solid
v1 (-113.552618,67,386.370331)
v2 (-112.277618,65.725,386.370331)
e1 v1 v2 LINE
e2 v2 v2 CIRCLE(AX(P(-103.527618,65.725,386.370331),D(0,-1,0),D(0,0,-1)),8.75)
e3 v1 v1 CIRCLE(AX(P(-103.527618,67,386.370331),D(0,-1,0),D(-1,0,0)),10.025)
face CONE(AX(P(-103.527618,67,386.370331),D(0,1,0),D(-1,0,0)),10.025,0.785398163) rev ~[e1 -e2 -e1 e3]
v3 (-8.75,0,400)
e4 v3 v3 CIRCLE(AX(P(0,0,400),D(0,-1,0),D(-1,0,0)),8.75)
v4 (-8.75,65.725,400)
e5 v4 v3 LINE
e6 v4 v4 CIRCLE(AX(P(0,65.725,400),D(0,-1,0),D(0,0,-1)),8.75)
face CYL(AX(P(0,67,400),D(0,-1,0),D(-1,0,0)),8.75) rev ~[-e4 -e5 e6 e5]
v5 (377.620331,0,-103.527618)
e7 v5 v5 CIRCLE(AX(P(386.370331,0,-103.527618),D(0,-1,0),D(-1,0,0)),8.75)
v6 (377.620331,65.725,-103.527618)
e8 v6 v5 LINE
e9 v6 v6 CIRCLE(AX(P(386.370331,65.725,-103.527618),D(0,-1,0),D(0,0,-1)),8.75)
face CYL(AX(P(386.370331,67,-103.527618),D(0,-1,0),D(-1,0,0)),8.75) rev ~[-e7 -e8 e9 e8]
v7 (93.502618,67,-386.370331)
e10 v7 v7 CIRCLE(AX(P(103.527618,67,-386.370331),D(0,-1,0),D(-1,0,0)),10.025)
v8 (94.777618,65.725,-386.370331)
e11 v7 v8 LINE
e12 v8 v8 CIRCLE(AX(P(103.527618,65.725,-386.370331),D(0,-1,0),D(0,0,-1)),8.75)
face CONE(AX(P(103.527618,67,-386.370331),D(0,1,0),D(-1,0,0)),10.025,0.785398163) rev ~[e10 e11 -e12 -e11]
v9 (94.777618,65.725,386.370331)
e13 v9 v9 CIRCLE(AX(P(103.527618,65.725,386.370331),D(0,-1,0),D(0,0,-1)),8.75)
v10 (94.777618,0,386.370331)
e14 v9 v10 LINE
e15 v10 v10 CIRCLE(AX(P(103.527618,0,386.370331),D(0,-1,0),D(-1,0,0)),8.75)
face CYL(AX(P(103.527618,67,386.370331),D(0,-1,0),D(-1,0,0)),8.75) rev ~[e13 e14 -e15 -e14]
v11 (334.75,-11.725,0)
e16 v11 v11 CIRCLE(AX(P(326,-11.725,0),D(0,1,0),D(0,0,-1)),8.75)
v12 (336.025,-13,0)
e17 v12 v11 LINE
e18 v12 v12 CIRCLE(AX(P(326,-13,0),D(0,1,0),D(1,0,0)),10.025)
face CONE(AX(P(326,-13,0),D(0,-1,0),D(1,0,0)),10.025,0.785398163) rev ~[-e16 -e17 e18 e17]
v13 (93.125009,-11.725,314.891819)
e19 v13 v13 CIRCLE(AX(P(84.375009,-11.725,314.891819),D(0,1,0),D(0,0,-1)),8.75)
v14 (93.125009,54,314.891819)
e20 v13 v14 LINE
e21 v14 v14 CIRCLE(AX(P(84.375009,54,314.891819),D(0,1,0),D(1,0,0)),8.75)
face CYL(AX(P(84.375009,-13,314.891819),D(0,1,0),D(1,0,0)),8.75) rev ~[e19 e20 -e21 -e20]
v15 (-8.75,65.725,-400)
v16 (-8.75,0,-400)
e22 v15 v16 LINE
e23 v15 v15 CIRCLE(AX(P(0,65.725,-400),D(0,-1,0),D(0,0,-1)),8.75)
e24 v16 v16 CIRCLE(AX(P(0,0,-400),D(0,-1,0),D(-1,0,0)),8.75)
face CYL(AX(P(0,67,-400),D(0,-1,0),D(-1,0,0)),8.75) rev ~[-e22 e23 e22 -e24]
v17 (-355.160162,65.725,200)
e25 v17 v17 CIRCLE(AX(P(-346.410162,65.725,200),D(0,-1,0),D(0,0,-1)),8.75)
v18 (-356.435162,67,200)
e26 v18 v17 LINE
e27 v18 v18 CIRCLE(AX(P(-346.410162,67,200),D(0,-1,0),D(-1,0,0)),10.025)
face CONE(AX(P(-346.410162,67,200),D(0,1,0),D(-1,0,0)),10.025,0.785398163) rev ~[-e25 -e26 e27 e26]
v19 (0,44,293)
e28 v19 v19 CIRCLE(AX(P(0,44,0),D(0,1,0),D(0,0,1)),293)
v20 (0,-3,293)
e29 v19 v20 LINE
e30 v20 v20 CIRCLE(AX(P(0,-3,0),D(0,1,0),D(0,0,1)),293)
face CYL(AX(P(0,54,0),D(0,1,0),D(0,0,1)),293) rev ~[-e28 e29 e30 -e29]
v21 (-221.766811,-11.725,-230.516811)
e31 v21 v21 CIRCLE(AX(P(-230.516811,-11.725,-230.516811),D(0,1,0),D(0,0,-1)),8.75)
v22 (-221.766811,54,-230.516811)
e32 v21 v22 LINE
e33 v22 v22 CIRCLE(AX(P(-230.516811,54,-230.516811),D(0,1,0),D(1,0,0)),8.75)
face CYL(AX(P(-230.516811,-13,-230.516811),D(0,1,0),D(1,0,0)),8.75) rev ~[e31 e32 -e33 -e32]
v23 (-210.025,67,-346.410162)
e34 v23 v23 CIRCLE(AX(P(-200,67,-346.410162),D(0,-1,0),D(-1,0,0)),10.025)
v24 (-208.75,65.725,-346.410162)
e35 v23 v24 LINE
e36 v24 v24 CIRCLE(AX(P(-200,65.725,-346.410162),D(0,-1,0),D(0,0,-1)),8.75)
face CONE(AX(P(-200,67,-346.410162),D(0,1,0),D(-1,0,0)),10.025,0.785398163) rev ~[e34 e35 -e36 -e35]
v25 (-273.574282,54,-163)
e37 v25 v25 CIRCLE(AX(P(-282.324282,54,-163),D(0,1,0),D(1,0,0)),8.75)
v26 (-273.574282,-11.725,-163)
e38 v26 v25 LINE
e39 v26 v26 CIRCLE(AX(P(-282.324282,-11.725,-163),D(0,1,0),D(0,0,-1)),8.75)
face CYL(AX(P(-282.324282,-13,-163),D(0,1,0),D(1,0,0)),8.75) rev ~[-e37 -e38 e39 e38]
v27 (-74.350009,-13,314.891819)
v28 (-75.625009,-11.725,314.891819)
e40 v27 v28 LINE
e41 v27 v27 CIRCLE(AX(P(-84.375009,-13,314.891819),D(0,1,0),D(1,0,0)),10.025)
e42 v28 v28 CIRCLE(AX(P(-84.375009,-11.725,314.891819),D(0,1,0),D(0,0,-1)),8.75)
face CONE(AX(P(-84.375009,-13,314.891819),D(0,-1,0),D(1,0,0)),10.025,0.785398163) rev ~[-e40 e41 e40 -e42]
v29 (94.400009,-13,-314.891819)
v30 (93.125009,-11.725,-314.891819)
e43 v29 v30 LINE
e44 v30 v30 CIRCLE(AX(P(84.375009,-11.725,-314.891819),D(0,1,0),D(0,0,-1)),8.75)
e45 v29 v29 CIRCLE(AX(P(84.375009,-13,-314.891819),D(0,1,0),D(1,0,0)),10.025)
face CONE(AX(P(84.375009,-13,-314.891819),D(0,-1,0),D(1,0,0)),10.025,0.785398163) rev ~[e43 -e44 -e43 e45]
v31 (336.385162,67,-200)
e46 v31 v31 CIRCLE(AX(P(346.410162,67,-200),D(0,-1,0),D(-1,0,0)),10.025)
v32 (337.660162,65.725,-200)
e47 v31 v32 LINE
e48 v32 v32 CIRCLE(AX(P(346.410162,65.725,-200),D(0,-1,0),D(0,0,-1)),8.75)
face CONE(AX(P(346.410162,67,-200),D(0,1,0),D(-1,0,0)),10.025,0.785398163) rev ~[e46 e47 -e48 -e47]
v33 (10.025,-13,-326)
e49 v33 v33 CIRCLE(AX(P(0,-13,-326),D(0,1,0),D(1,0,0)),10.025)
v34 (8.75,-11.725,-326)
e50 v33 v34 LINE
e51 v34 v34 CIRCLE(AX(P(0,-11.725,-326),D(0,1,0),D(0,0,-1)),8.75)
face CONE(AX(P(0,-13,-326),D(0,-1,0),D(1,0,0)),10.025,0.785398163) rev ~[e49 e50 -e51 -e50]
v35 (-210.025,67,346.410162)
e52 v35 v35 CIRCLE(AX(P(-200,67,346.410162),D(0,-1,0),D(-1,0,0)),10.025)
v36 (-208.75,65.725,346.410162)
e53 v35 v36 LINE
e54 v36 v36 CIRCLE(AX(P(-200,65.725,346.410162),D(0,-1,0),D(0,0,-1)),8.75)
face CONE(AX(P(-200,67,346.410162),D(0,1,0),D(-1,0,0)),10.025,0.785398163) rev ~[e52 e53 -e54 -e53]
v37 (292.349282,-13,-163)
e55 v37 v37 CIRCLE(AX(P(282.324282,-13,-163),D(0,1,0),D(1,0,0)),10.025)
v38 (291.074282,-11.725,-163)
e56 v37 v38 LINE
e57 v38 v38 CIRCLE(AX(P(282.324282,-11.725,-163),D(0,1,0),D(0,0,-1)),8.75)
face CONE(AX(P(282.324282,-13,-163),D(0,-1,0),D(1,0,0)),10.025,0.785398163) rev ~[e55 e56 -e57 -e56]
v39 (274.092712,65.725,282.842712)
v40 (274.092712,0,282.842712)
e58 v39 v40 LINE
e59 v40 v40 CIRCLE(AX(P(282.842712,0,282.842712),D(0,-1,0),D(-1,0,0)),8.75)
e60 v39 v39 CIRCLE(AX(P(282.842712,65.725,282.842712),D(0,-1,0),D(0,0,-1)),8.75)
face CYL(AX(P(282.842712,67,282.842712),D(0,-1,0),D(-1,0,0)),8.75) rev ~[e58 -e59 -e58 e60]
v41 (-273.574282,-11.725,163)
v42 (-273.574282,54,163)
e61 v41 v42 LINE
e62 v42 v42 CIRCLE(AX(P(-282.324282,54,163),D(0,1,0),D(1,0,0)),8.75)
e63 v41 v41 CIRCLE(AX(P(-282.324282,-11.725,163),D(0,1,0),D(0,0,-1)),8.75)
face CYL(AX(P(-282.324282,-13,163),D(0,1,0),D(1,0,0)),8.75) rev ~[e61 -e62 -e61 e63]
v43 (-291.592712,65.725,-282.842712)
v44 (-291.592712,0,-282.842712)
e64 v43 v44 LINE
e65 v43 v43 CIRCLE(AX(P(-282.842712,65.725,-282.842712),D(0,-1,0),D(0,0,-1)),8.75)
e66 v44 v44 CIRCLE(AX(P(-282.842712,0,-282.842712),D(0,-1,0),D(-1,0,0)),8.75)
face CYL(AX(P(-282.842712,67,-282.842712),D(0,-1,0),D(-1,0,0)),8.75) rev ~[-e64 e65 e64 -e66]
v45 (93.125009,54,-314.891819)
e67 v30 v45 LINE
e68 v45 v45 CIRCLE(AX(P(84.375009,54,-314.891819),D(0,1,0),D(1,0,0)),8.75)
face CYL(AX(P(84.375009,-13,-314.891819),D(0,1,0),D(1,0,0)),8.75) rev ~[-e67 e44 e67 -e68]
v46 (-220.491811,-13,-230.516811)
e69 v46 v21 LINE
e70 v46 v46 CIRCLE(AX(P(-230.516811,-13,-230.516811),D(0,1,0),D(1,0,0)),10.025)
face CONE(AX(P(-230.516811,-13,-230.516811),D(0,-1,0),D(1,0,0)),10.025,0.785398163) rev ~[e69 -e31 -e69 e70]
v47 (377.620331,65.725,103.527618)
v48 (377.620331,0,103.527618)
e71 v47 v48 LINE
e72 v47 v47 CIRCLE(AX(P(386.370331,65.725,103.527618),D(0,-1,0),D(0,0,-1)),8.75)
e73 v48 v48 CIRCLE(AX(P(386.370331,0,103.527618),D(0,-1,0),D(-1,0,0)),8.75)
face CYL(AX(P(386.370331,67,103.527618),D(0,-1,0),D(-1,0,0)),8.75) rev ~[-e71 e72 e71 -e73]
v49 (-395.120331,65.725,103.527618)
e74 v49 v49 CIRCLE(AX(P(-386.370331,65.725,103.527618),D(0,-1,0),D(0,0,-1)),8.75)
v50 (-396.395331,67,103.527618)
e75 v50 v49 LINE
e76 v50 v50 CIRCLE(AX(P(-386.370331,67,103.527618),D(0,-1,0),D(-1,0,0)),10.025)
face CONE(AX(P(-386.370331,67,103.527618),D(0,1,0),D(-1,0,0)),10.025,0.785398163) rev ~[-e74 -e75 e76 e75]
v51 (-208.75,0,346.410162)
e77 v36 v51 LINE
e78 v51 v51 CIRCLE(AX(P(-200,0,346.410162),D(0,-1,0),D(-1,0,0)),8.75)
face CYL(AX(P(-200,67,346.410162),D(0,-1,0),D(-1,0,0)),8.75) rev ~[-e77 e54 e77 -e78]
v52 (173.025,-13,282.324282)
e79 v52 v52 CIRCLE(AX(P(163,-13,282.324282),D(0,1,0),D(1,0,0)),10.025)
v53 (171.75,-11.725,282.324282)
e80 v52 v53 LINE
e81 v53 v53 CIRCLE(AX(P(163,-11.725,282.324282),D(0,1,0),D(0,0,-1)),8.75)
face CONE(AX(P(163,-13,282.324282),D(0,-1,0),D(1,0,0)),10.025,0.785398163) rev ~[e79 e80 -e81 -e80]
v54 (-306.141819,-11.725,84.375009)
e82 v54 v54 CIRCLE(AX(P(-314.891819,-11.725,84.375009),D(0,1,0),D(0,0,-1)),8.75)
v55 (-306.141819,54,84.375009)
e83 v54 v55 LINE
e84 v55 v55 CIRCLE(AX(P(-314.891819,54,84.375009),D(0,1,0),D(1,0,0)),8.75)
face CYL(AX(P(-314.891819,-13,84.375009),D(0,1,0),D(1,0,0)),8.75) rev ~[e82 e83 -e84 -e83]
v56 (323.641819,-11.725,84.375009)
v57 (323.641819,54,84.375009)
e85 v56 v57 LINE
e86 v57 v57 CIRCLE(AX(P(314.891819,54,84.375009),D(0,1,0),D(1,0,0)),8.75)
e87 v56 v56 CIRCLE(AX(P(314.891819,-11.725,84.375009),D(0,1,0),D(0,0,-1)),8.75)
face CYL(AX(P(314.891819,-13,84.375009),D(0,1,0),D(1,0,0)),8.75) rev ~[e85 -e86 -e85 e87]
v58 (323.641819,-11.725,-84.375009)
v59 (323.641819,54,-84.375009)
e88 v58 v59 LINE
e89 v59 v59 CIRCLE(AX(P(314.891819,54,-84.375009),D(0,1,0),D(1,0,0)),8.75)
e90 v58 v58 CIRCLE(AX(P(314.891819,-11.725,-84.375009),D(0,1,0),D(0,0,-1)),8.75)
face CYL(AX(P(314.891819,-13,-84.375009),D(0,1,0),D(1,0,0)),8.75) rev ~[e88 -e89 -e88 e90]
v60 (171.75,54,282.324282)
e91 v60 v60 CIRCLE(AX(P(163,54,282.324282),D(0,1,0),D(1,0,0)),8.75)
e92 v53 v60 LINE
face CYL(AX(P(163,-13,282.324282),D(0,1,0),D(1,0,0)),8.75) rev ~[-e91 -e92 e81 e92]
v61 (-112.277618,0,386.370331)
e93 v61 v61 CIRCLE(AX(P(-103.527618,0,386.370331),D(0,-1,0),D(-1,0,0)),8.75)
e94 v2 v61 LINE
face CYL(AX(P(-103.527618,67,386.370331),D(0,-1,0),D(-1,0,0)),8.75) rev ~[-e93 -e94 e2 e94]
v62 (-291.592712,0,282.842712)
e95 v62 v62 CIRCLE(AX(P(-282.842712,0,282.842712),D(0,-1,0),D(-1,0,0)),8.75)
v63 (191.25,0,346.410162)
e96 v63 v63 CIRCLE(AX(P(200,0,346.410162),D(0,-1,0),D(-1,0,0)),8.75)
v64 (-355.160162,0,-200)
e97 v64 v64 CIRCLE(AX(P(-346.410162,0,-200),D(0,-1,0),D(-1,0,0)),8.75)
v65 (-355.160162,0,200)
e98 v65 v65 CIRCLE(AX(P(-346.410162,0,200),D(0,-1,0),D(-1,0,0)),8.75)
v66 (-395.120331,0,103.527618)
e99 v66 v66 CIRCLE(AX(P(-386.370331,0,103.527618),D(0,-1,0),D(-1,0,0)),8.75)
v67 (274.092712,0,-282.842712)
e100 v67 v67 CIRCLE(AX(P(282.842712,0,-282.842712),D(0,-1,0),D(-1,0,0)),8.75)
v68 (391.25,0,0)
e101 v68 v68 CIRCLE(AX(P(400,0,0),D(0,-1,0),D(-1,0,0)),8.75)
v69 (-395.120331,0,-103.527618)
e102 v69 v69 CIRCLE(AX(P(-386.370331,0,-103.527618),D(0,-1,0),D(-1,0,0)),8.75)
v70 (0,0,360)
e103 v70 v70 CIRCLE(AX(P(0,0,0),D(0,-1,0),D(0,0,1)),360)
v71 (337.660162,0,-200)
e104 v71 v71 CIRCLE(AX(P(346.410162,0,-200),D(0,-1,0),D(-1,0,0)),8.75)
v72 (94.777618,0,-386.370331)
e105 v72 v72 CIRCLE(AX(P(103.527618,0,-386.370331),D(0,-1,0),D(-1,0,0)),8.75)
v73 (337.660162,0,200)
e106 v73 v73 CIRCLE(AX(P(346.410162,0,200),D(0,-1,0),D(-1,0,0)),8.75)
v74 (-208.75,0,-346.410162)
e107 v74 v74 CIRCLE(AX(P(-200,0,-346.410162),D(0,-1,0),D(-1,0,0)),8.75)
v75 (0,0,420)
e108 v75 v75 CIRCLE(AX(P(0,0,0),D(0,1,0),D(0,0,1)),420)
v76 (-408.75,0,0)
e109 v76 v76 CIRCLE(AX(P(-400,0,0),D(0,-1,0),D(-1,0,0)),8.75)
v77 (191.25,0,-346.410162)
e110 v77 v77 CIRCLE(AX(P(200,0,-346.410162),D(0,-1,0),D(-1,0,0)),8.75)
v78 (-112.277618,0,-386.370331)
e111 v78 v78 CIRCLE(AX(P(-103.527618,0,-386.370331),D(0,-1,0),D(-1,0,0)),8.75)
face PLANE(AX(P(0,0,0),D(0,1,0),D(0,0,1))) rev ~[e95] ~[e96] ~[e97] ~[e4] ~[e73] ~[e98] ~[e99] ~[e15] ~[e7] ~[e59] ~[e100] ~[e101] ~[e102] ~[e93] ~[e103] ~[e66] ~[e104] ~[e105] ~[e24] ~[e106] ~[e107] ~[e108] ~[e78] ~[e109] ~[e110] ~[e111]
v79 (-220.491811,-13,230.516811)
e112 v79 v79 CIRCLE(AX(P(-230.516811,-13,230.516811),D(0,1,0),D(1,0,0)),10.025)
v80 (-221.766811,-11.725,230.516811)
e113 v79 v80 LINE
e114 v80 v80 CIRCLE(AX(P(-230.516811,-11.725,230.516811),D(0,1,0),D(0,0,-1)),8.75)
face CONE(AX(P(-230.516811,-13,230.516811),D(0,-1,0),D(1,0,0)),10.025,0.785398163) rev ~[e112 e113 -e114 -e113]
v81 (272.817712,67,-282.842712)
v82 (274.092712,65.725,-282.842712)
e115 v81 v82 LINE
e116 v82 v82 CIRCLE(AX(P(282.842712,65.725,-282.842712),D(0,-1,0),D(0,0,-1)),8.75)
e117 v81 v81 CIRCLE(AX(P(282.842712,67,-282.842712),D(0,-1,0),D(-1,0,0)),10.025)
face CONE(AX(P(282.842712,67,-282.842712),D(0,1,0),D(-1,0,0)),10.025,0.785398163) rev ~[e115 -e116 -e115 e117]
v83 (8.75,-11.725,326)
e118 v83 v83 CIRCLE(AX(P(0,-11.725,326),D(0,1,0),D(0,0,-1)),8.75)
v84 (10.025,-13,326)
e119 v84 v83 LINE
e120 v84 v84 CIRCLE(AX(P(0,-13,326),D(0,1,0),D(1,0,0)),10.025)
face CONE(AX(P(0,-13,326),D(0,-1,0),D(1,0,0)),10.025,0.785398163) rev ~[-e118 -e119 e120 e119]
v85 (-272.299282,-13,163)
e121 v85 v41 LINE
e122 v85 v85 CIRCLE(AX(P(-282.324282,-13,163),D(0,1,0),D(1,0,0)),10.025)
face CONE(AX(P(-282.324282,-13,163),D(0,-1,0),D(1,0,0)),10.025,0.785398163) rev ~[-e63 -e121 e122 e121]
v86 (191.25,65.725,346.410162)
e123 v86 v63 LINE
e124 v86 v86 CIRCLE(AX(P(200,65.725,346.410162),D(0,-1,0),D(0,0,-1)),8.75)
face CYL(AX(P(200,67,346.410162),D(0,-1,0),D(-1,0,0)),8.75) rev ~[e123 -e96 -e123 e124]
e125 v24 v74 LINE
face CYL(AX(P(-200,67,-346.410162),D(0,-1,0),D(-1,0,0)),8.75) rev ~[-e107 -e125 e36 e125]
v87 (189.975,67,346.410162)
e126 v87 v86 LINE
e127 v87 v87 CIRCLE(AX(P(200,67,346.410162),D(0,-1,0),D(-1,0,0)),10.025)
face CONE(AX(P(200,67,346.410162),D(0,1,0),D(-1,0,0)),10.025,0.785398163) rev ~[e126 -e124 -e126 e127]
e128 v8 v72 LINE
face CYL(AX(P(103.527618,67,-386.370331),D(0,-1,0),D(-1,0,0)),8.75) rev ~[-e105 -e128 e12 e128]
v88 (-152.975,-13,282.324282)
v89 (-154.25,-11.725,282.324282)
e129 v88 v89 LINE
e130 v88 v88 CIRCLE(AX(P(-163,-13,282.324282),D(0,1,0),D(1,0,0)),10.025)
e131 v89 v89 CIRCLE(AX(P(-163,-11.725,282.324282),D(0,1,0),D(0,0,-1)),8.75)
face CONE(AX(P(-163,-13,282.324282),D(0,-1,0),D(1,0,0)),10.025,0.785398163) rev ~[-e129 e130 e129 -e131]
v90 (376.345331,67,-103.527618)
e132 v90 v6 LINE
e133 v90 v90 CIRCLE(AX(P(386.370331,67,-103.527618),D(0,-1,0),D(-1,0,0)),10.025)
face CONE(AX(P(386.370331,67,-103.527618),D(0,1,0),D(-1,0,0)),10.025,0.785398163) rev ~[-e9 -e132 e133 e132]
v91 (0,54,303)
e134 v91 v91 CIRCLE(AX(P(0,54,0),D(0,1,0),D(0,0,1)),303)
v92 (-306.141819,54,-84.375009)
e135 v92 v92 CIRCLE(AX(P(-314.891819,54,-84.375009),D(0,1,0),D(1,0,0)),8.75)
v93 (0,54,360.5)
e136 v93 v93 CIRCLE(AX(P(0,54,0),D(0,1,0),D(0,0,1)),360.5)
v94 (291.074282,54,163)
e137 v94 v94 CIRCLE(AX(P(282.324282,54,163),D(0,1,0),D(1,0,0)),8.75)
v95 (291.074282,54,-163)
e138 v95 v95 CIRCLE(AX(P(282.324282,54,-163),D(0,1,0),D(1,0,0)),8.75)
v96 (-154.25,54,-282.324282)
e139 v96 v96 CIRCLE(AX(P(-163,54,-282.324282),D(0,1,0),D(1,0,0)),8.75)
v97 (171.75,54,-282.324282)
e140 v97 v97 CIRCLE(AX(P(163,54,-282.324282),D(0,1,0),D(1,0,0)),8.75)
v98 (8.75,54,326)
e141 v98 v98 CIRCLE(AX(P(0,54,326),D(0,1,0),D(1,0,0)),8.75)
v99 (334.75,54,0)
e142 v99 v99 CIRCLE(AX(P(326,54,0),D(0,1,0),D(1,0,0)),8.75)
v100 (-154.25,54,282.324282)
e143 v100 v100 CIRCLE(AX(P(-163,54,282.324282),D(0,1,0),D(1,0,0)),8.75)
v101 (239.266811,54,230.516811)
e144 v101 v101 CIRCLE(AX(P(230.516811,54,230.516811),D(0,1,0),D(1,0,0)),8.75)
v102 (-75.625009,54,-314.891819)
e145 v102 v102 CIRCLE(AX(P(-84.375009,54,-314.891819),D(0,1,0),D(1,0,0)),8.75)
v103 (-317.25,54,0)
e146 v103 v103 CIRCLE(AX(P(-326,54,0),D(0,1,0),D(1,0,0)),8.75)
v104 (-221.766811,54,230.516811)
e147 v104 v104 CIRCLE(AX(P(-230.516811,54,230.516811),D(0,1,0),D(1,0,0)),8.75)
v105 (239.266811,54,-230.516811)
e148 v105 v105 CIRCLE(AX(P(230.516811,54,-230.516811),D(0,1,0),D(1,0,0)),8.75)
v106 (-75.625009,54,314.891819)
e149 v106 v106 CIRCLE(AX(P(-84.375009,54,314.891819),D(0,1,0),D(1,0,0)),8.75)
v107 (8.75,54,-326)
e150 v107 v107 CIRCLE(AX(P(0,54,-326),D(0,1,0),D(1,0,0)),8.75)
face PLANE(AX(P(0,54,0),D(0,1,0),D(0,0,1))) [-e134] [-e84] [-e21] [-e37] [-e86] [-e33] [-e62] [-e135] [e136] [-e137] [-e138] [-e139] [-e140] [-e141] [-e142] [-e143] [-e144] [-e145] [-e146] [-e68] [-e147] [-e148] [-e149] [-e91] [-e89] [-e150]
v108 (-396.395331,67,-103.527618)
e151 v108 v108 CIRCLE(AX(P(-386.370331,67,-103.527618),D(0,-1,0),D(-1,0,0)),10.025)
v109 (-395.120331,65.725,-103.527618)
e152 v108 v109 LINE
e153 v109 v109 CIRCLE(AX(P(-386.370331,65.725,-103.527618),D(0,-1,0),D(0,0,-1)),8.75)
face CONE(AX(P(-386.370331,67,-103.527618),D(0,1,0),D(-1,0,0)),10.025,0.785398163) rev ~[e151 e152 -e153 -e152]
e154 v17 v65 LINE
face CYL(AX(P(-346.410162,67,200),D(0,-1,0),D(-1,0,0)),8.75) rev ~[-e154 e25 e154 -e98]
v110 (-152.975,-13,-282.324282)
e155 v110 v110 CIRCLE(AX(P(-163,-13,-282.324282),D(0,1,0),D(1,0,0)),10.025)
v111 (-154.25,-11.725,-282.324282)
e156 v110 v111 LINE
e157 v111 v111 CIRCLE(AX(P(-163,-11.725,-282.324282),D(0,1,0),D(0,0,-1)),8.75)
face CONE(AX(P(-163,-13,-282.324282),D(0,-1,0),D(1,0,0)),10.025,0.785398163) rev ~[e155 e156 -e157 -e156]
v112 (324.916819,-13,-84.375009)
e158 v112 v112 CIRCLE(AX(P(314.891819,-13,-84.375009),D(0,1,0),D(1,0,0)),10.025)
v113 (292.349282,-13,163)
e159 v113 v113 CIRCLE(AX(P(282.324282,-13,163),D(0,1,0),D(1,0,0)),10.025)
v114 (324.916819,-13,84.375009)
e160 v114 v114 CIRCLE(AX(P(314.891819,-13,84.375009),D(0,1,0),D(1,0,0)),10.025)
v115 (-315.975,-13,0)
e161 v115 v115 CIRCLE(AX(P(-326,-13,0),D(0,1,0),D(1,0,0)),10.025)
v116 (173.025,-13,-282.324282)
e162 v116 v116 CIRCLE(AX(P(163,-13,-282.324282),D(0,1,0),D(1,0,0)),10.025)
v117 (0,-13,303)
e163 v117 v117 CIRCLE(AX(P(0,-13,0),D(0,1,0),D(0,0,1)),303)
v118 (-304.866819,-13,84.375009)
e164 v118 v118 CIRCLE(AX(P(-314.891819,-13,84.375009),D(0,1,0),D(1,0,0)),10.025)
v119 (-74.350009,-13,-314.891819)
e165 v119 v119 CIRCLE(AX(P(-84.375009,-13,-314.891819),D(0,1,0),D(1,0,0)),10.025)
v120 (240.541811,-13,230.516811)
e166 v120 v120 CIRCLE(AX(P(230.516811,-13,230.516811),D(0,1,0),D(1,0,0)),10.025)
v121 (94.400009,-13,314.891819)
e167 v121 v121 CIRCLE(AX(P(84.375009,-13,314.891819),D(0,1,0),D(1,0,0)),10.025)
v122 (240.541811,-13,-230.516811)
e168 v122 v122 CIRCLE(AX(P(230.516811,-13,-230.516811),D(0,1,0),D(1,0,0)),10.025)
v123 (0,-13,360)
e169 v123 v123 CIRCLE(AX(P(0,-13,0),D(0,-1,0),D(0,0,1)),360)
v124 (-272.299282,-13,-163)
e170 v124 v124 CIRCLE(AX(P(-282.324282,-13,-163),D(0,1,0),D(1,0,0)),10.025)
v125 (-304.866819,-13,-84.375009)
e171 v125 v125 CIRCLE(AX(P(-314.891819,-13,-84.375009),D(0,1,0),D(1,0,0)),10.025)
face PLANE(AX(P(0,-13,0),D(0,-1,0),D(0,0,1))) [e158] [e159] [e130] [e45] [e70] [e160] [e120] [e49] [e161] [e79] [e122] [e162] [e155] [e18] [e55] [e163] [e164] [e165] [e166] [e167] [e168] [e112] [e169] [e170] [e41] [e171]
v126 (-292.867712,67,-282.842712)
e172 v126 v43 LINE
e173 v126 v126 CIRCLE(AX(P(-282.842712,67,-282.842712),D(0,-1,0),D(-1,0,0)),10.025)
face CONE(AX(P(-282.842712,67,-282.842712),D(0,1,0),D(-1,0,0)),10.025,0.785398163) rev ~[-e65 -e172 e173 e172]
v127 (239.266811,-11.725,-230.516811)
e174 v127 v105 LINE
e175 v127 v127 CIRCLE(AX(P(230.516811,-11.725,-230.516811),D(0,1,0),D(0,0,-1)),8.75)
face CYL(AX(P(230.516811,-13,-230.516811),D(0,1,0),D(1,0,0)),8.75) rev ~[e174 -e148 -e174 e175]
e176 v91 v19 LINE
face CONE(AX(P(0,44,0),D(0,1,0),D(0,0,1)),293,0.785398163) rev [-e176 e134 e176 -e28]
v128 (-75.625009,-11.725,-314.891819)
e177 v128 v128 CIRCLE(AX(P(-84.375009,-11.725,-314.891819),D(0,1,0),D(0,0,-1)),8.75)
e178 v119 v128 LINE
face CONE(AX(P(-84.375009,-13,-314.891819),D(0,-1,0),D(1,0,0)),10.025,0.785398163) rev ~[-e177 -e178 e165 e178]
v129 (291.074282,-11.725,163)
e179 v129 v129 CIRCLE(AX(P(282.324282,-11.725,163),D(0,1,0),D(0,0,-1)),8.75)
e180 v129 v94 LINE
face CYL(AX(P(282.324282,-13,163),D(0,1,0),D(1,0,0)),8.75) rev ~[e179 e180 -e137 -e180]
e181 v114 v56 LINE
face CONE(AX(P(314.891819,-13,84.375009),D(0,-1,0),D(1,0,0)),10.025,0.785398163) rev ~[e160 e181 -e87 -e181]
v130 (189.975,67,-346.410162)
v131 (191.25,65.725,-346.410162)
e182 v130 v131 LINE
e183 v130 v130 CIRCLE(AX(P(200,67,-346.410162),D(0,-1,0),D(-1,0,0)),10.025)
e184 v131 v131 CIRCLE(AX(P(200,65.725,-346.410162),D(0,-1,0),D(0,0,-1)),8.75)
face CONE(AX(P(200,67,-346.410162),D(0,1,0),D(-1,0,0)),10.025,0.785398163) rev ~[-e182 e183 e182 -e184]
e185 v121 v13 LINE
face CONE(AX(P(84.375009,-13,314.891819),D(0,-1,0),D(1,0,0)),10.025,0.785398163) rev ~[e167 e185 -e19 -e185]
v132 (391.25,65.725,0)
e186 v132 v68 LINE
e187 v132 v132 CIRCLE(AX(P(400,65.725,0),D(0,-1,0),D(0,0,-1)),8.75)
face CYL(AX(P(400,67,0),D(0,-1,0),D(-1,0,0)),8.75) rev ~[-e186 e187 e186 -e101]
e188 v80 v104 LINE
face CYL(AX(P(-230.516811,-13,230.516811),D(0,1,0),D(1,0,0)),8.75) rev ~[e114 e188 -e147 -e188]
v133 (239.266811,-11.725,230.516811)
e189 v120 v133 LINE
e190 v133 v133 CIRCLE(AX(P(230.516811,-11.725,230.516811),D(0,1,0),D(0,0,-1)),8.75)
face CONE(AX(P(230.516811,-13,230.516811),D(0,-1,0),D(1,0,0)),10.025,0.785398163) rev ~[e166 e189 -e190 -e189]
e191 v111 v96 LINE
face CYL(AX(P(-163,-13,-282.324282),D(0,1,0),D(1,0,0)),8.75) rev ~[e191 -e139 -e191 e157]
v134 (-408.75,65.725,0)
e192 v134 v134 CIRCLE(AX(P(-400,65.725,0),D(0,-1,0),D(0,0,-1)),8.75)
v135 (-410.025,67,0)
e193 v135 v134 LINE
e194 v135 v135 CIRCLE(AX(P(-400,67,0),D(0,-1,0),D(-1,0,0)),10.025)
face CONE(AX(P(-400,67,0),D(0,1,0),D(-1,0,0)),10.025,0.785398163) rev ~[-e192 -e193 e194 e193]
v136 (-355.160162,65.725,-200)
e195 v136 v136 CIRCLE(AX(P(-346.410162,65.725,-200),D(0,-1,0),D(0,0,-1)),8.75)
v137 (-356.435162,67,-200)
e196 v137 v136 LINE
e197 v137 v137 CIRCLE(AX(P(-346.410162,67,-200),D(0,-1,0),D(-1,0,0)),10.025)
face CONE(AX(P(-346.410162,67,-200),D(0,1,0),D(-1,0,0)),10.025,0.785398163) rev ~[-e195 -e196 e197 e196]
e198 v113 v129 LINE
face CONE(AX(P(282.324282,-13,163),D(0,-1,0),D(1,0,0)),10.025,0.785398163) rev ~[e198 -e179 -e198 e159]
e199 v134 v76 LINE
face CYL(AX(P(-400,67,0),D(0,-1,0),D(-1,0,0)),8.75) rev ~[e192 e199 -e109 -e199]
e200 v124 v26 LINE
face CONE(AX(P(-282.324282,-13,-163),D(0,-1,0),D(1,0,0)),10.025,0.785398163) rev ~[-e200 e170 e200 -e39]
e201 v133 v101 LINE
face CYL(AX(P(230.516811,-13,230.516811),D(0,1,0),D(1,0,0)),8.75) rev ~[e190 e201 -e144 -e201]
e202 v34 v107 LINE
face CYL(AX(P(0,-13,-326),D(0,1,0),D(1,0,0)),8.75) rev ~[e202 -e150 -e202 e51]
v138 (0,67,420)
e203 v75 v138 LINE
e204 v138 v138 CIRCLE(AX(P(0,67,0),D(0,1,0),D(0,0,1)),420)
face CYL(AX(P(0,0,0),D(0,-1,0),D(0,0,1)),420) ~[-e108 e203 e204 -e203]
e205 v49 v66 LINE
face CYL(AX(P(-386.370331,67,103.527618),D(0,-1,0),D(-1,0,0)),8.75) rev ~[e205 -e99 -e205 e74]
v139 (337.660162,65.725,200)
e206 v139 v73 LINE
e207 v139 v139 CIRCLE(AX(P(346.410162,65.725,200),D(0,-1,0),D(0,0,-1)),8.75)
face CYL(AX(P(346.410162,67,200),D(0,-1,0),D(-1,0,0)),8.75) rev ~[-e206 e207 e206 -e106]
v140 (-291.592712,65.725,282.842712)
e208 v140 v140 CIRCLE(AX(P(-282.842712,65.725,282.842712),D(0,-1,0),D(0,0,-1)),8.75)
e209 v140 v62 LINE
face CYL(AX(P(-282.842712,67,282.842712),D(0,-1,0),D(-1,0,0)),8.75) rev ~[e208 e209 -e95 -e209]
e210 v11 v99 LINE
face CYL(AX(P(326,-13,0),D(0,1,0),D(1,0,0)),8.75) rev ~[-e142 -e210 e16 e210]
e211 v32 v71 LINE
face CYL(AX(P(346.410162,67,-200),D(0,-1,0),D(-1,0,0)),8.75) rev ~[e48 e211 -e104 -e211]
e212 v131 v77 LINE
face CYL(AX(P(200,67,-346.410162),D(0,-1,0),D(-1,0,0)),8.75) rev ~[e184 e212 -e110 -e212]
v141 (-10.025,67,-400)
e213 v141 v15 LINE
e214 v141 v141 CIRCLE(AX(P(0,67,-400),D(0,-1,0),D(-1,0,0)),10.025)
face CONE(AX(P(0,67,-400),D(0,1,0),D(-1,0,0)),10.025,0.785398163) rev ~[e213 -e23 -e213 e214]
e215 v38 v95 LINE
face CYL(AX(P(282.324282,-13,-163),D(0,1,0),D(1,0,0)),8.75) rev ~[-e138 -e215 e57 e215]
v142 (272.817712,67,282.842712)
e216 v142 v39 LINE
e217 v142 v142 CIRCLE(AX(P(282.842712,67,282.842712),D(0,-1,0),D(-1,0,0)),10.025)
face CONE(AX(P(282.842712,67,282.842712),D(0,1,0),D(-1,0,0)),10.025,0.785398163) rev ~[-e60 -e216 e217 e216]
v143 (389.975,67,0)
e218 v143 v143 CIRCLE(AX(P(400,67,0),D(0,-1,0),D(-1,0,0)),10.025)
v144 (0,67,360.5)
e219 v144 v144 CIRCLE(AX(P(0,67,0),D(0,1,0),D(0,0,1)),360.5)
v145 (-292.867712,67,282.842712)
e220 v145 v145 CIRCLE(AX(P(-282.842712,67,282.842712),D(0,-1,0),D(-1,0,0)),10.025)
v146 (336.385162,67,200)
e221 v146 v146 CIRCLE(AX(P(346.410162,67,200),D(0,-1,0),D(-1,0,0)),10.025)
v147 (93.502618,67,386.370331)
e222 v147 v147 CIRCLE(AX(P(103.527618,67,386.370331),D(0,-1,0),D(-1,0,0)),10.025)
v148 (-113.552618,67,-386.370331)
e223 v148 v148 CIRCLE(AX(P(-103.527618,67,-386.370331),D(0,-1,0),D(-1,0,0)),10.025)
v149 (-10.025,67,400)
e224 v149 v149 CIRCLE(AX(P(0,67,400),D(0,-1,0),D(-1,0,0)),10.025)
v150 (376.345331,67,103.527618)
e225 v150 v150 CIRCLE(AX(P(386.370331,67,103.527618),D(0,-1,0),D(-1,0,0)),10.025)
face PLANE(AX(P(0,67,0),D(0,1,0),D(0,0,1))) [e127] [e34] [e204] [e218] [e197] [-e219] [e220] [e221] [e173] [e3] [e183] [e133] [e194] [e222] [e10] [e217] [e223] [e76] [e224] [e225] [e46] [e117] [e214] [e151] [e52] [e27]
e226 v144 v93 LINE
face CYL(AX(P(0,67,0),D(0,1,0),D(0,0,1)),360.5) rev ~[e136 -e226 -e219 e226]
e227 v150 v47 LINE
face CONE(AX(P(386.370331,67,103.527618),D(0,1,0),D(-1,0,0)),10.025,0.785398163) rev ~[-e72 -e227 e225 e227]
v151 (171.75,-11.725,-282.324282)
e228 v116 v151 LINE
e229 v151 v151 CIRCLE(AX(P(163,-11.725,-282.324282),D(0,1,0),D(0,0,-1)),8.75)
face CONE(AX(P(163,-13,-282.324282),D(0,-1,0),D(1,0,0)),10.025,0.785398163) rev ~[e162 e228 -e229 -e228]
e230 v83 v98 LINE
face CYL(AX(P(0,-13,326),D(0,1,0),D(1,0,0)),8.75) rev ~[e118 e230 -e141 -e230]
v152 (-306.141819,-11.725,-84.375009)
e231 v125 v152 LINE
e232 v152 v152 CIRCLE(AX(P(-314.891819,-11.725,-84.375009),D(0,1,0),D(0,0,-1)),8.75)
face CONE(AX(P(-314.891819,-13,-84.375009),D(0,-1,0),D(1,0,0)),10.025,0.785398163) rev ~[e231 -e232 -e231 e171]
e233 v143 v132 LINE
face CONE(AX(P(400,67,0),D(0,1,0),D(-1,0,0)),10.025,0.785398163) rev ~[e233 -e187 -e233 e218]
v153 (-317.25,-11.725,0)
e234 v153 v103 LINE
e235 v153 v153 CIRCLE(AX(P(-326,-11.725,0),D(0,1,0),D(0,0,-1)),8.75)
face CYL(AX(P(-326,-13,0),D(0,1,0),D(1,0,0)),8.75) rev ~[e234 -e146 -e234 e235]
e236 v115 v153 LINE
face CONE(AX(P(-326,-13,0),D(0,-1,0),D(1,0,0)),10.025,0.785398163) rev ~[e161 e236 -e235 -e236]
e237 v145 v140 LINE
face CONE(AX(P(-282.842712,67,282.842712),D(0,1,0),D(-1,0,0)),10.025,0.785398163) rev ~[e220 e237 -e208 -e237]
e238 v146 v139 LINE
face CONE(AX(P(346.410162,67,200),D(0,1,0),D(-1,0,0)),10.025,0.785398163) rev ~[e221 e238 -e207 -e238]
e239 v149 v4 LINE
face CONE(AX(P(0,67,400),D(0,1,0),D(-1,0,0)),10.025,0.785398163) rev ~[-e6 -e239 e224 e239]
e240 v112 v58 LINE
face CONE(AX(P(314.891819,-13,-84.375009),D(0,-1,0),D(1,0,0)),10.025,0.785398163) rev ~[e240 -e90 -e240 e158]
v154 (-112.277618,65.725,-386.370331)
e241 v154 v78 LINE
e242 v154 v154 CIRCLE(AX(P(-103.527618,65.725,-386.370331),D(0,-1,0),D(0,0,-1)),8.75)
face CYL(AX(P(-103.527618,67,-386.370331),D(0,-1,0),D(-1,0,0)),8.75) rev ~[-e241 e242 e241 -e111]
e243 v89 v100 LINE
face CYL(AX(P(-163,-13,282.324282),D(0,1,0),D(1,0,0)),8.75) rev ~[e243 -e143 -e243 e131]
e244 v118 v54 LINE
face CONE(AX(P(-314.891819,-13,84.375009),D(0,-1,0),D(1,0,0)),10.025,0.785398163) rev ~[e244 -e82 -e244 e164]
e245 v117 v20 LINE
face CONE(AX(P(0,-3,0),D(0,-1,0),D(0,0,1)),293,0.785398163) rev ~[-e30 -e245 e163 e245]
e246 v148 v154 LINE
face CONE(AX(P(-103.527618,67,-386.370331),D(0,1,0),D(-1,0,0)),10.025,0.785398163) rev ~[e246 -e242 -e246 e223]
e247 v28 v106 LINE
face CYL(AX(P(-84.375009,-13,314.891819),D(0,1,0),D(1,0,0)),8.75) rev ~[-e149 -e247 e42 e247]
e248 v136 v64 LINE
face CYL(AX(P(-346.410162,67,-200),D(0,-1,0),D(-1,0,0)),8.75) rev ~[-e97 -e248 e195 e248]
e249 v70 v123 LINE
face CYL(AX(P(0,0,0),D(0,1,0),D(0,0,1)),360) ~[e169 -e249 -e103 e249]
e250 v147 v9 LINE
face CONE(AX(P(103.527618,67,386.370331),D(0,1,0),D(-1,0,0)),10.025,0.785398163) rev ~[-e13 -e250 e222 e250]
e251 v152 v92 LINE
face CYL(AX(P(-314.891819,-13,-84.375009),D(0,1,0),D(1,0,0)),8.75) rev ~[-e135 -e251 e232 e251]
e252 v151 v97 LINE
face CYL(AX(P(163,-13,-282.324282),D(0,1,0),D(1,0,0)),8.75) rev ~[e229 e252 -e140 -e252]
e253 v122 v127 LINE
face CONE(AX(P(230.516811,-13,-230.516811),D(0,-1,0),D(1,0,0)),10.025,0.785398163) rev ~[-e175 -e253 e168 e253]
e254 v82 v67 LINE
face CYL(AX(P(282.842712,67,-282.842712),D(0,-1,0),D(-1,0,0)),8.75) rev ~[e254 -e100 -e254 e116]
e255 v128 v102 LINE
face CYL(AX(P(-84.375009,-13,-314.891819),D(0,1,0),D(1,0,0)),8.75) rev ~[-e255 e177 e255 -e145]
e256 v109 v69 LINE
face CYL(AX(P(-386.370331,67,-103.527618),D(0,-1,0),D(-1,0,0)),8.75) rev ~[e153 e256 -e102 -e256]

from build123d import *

# Parameters (mm, degrees)
SKETCH1_R                    = 420
BOSS_EXTRUDE1_DEPTH          = 67
SKETCH2_R                    = 360.5
CUT_EXTRUDE1_DEPTH           = 13
SKETCH3_R                    = 360
BOSS_EXTRUDE2_DEPTH          = 13
M20_TAPPED_HOLE1_D           = 17.5
M20_TAPPED_HOLE1_CSINK_D     = 20.05
M20_TAPPED_HOLE1_CSINK_ANGLE = 90
SKETCH6_R                    = 293
CUT_EXTRUDE2_DEPTH           = 598.736564048
CHAMFER1_SIZE                = 10
M20_TAPPED_HOLE2_D           = 17.5
M20_TAPPED_HOLE2_CSINK_D     = 20.05
M20_TAPPED_HOLE2_CSINK_ANGLE = 90


with BuildPart() as part:
    # Sketch1 → Boss-Extrude1 (new body)
    with BuildSketch(Plane(origin=(0, 0, 0), x_dir=(1, 0, 0), z_dir=(0, 1, 0))):
        with Locations(Location((0, 0, 0), (0, 0, 270))):
            Circle(SKETCH1_R)
    extrude(amount=BOSS_EXTRUDE1_DEPTH)

    # Sketch2 → Cut-Extrude1 (cut)
    with BuildSketch(Plane(origin=(0, 67, 0), x_dir=(1, 0, 0), z_dir=(0, 1, 0))):
        with Locations(Location((0, 0, 0), (0, 0, 270))):
            Circle(SKETCH2_R)
    extrude(amount=-CUT_EXTRUDE1_DEPTH, mode=Mode.SUBTRACT)

    # Sketch3 → Boss-Extrude2 (add)
    with BuildSketch(Plane.XZ):
        with Locations(Location((0, 0, 0), (0, 0, 90))):
            Circle(SKETCH3_R)
    extrude(amount=BOSS_EXTRUDE2_DEPTH)

    # M20 Tapped Hole1 (through all)
    with Locations(Plane(origin=(0, 67, 0), x_dir=(1, 0, 0), z_dir=(0, 1, 0))):
        with Locations((-103.527618041, 386.370330516), (0, 400), (103.527618041, 386.370330516), (200, 346.410161514), (282.842712475, 282.842712475), (346.410161514, 200), (386.370330516, 103.527618041), (400, 0), (386.370330516, -103.527618041), (346.410161514, -200), (282.842712475, -282.842712475), (200, -346.410161514), (103.527618041, -386.370330516), (0, -400), (-103.527618041, -386.370330516), (-200, -346.410161514), (-282.842712475, -282.842712475), (-346.410161514, -200), (-386.370330516, -103.527618041), (-400, 0), (-386.370330516, 103.527618041), (-346.410161514, 200), (-282.842712475, 282.842712475), (-200, 346.410161514)):
            CounterSinkHole(M20_TAPPED_HOLE1_D / 2, M20_TAPPED_HOLE1_CSINK_D / 2, counter_sink_angle=M20_TAPPED_HOLE1_CSINK_ANGLE)

    # Sketch6 → Cut-Extrude2 (cut, through all)
    with BuildSketch(Plane(origin=(0, 54, 0), x_dir=(1, 0, 0), z_dir=(0, 1, 0))):
        with Locations(Location((0, 0, 0), (0, 0, 270))):
            Circle(SKETCH6_R)
    extrude(amount=-CUT_EXTRUDE2_DEPTH, mode=Mode.SUBTRACT)

    # Chamfer1
    chamfer1_edges = [part.edges().sort_by_distance(p)[0] for p in [
        (0, -13, -293),
        (0, 54, -293),
    ]]
    chamfer(chamfer1_edges, length=CHAMFER1_SIZE)

    # M20 Tapped Hole2 (through all)
    with Locations(Plane(origin=(0, -13, 0), x_dir=(-1, 0, 0), z_dir=(0, -1, 0))):
        with Locations((-84.375008703, 314.89181937), (0, 326), (84.375008703, 314.89181937), (163, 282.324281634), (230.516810667, 230.516810667), (282.324281634, 163), (314.89181937, 84.375008703), (326, 0), (314.89181937, -84.375008703), (282.324281634, -163), (230.516810667, -230.516810667), (163, -282.324281634), (84.375008703, -314.89181937), (0, -326), (-84.375008703, -314.89181937), (-163, -282.324281634), (-230.516810667, -230.516810667), (-282.324281634, -163), (-314.89181937, -84.375008703), (-326, 0), (-314.89181937, 84.375008703), (-282.324281634, 163), (-230.516810667, 230.516810667), (-163, 282.324281634)):
            CounterSinkHole(M20_TAPPED_HOLE2_D / 2, M20_TAPPED_HOLE2_CSINK_D / 2, counter_sink_angle=M20_TAPPED_HOLE2_CSINK_ANGLE)


solid = part.part
